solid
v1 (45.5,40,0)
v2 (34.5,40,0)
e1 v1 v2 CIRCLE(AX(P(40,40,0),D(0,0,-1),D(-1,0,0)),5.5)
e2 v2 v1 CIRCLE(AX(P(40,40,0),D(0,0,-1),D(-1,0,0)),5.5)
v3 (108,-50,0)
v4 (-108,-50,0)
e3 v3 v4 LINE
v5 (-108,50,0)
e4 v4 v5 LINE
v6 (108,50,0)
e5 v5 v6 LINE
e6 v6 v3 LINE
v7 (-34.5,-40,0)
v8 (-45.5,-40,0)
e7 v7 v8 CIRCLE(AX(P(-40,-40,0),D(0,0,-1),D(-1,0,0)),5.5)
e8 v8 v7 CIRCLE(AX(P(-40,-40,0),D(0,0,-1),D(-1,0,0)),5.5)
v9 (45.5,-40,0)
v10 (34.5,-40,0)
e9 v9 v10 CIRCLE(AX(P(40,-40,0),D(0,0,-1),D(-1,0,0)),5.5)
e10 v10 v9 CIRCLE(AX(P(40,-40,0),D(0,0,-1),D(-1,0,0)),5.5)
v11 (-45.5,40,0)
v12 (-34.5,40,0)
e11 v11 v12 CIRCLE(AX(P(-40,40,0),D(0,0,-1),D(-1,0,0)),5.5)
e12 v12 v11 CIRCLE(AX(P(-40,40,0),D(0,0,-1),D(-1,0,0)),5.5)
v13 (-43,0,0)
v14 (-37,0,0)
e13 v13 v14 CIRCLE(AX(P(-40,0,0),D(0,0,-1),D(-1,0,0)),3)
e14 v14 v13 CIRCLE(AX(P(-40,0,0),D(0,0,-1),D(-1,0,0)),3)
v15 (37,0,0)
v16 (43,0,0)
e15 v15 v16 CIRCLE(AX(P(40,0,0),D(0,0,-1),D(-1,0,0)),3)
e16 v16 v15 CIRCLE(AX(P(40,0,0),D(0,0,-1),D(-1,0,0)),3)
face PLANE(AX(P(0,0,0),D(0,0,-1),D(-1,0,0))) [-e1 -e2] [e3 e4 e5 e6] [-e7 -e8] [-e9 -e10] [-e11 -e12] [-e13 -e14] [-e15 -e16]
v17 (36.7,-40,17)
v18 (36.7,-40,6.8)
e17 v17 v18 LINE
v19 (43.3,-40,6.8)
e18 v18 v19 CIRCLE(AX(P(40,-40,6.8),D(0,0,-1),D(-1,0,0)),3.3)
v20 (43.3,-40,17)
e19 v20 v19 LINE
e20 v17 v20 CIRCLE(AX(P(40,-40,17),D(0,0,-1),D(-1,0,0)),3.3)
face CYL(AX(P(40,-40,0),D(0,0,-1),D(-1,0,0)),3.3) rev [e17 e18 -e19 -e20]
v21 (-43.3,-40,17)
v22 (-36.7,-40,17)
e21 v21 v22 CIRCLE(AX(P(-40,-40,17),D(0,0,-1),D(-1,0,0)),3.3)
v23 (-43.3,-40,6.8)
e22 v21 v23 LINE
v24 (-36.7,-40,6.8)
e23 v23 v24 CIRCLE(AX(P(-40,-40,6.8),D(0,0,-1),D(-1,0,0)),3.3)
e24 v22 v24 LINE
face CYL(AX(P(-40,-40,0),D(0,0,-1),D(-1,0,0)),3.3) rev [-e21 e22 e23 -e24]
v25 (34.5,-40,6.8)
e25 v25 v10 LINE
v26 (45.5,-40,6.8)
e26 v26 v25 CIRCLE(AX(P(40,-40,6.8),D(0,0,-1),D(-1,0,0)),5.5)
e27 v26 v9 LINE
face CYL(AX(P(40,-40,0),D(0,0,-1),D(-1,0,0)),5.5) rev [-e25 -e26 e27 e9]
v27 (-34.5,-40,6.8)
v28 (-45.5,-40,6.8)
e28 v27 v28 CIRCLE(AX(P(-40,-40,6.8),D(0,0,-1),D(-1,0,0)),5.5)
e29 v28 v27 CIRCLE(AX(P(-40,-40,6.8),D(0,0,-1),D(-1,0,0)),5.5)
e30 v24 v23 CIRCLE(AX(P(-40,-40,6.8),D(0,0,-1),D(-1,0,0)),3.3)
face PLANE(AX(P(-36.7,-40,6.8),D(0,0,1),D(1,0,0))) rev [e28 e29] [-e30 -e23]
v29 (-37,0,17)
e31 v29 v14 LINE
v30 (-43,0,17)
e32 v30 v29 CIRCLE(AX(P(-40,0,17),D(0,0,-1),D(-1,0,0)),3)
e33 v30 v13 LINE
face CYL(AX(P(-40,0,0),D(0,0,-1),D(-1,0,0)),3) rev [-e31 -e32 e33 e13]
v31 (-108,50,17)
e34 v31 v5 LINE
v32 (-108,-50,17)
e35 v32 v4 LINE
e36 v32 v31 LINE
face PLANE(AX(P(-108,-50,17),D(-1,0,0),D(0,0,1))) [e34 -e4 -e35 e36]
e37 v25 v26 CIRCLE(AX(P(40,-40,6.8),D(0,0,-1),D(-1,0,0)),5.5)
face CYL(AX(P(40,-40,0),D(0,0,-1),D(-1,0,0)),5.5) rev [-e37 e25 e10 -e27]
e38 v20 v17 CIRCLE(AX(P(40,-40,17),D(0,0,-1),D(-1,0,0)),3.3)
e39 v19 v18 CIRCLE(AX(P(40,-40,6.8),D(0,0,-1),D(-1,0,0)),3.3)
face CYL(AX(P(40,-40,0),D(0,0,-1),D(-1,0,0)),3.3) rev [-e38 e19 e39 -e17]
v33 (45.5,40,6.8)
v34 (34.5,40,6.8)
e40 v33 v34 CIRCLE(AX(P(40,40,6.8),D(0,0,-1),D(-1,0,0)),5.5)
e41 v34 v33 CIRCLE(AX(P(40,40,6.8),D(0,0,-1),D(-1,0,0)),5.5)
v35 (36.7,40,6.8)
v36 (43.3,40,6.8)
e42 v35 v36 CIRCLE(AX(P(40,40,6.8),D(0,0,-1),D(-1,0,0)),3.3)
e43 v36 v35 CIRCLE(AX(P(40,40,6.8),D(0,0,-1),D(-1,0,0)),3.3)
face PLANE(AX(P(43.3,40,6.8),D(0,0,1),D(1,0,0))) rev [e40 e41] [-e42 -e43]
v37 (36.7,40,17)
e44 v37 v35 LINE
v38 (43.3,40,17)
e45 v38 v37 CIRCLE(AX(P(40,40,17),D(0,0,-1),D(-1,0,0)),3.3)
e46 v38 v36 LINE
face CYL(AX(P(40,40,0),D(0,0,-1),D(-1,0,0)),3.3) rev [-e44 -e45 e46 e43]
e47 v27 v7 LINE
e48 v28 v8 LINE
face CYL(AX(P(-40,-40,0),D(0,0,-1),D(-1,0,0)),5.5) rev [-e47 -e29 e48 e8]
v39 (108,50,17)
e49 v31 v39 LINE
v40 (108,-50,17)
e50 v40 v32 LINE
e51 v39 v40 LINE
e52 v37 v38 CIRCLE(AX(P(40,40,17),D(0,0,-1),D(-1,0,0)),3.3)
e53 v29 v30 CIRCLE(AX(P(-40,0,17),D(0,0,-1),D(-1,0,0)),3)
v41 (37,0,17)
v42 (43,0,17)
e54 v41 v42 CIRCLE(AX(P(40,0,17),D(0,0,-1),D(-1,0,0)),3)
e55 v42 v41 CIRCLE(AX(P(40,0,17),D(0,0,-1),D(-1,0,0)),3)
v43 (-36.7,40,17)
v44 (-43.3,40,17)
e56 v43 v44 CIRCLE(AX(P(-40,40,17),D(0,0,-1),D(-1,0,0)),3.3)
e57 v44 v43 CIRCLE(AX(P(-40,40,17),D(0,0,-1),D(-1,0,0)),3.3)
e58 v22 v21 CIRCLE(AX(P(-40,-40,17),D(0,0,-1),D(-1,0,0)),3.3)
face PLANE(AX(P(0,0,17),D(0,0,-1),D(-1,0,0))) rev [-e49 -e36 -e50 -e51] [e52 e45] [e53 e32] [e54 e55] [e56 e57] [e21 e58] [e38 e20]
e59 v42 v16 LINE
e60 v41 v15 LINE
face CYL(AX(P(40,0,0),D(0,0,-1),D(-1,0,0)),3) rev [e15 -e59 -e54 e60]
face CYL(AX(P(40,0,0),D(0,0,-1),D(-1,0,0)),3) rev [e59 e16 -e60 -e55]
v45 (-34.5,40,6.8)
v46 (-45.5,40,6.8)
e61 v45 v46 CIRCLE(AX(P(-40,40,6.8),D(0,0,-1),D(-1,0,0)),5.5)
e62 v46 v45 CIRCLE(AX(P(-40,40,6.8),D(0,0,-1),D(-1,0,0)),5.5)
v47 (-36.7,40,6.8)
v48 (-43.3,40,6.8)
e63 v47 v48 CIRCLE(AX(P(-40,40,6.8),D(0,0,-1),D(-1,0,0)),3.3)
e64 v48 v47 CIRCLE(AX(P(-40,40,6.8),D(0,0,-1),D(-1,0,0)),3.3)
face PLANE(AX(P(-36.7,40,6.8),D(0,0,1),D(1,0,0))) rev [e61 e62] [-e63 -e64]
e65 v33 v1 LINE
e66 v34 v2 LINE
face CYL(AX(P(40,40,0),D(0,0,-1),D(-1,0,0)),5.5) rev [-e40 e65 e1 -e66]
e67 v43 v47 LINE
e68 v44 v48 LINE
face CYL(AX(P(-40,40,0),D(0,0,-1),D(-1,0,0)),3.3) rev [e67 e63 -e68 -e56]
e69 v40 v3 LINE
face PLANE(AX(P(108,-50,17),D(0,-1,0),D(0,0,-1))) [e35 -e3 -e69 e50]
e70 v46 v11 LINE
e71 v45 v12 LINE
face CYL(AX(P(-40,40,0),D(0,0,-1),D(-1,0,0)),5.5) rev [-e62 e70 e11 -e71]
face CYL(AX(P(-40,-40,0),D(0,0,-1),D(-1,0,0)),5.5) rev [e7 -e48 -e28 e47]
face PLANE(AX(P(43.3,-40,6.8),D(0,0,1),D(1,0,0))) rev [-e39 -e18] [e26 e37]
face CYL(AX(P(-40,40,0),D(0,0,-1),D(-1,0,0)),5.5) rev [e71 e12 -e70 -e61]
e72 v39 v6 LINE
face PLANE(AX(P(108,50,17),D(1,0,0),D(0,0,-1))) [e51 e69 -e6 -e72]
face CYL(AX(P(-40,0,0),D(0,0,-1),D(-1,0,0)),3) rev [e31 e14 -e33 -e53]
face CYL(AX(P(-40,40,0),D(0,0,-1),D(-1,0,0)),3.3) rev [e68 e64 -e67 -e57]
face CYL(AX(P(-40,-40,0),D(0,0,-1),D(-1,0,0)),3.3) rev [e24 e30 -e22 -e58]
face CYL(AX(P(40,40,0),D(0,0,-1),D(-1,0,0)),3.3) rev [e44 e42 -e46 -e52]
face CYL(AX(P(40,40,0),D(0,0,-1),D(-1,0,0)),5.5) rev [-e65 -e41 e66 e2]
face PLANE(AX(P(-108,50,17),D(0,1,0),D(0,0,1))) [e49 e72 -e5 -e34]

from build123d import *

# Parameters (mm, degrees)
SKETCH1_W                               = 216
SKETCH1_H                               = 100
BOSS_EXTRUDE1_DEPTH                     = 17
F_6_0_6_DIAMETER_HOLE1_D                = 6
CBORE_FOR_M6_HEX_HEAD_BOLT1_D           = 6.6
CBORE_FOR_M6_HEX_HEAD_BOLT1_CBORE_D     = 11
CBORE_FOR_M6_HEX_HEAD_BOLT1_CBORE_DEPTH = 6.8


with BuildPart() as part:
    # Sketch1 → Boss-Extrude1 (new body)
    with BuildSketch(Plane(origin=(0, 0, 0), x_dir=(-1, 0, 0), z_dir=(0, 0, -1))):
        Rectangle(SKETCH1_W, SKETCH1_H)
    extrude(amount=-BOSS_EXTRUDE1_DEPTH)

    # Ø6.0 (6) Diameter Hole1 (through all)
    with Locations(Plane(origin=(0, 0, 0), x_dir=(-1, 0, 0), z_dir=(0, 0, -1))):
        with Locations((-40, 0), (40, 0)):
            Hole(F_6_0_6_DIAMETER_HOLE1_D / 2)

    # CBORE for M6 Hex Head Bolt1 (through all)
    with Locations(Plane(origin=(0, 0, 0), x_dir=(-1, 0, 0), z_dir=(0, 0, -1))):
        with Locations((40, 40), (40, -40), (-40, -40), (-40, 40)):
            CounterBoreHole(CBORE_FOR_M6_HEX_HEAD_BOLT1_D / 2, CBORE_FOR_M6_HEX_HEAD_BOLT1_CBORE_D / 2, CBORE_FOR_M6_HEX_HEAD_BOLT1_CBORE_DEPTH)


solid = part.part
